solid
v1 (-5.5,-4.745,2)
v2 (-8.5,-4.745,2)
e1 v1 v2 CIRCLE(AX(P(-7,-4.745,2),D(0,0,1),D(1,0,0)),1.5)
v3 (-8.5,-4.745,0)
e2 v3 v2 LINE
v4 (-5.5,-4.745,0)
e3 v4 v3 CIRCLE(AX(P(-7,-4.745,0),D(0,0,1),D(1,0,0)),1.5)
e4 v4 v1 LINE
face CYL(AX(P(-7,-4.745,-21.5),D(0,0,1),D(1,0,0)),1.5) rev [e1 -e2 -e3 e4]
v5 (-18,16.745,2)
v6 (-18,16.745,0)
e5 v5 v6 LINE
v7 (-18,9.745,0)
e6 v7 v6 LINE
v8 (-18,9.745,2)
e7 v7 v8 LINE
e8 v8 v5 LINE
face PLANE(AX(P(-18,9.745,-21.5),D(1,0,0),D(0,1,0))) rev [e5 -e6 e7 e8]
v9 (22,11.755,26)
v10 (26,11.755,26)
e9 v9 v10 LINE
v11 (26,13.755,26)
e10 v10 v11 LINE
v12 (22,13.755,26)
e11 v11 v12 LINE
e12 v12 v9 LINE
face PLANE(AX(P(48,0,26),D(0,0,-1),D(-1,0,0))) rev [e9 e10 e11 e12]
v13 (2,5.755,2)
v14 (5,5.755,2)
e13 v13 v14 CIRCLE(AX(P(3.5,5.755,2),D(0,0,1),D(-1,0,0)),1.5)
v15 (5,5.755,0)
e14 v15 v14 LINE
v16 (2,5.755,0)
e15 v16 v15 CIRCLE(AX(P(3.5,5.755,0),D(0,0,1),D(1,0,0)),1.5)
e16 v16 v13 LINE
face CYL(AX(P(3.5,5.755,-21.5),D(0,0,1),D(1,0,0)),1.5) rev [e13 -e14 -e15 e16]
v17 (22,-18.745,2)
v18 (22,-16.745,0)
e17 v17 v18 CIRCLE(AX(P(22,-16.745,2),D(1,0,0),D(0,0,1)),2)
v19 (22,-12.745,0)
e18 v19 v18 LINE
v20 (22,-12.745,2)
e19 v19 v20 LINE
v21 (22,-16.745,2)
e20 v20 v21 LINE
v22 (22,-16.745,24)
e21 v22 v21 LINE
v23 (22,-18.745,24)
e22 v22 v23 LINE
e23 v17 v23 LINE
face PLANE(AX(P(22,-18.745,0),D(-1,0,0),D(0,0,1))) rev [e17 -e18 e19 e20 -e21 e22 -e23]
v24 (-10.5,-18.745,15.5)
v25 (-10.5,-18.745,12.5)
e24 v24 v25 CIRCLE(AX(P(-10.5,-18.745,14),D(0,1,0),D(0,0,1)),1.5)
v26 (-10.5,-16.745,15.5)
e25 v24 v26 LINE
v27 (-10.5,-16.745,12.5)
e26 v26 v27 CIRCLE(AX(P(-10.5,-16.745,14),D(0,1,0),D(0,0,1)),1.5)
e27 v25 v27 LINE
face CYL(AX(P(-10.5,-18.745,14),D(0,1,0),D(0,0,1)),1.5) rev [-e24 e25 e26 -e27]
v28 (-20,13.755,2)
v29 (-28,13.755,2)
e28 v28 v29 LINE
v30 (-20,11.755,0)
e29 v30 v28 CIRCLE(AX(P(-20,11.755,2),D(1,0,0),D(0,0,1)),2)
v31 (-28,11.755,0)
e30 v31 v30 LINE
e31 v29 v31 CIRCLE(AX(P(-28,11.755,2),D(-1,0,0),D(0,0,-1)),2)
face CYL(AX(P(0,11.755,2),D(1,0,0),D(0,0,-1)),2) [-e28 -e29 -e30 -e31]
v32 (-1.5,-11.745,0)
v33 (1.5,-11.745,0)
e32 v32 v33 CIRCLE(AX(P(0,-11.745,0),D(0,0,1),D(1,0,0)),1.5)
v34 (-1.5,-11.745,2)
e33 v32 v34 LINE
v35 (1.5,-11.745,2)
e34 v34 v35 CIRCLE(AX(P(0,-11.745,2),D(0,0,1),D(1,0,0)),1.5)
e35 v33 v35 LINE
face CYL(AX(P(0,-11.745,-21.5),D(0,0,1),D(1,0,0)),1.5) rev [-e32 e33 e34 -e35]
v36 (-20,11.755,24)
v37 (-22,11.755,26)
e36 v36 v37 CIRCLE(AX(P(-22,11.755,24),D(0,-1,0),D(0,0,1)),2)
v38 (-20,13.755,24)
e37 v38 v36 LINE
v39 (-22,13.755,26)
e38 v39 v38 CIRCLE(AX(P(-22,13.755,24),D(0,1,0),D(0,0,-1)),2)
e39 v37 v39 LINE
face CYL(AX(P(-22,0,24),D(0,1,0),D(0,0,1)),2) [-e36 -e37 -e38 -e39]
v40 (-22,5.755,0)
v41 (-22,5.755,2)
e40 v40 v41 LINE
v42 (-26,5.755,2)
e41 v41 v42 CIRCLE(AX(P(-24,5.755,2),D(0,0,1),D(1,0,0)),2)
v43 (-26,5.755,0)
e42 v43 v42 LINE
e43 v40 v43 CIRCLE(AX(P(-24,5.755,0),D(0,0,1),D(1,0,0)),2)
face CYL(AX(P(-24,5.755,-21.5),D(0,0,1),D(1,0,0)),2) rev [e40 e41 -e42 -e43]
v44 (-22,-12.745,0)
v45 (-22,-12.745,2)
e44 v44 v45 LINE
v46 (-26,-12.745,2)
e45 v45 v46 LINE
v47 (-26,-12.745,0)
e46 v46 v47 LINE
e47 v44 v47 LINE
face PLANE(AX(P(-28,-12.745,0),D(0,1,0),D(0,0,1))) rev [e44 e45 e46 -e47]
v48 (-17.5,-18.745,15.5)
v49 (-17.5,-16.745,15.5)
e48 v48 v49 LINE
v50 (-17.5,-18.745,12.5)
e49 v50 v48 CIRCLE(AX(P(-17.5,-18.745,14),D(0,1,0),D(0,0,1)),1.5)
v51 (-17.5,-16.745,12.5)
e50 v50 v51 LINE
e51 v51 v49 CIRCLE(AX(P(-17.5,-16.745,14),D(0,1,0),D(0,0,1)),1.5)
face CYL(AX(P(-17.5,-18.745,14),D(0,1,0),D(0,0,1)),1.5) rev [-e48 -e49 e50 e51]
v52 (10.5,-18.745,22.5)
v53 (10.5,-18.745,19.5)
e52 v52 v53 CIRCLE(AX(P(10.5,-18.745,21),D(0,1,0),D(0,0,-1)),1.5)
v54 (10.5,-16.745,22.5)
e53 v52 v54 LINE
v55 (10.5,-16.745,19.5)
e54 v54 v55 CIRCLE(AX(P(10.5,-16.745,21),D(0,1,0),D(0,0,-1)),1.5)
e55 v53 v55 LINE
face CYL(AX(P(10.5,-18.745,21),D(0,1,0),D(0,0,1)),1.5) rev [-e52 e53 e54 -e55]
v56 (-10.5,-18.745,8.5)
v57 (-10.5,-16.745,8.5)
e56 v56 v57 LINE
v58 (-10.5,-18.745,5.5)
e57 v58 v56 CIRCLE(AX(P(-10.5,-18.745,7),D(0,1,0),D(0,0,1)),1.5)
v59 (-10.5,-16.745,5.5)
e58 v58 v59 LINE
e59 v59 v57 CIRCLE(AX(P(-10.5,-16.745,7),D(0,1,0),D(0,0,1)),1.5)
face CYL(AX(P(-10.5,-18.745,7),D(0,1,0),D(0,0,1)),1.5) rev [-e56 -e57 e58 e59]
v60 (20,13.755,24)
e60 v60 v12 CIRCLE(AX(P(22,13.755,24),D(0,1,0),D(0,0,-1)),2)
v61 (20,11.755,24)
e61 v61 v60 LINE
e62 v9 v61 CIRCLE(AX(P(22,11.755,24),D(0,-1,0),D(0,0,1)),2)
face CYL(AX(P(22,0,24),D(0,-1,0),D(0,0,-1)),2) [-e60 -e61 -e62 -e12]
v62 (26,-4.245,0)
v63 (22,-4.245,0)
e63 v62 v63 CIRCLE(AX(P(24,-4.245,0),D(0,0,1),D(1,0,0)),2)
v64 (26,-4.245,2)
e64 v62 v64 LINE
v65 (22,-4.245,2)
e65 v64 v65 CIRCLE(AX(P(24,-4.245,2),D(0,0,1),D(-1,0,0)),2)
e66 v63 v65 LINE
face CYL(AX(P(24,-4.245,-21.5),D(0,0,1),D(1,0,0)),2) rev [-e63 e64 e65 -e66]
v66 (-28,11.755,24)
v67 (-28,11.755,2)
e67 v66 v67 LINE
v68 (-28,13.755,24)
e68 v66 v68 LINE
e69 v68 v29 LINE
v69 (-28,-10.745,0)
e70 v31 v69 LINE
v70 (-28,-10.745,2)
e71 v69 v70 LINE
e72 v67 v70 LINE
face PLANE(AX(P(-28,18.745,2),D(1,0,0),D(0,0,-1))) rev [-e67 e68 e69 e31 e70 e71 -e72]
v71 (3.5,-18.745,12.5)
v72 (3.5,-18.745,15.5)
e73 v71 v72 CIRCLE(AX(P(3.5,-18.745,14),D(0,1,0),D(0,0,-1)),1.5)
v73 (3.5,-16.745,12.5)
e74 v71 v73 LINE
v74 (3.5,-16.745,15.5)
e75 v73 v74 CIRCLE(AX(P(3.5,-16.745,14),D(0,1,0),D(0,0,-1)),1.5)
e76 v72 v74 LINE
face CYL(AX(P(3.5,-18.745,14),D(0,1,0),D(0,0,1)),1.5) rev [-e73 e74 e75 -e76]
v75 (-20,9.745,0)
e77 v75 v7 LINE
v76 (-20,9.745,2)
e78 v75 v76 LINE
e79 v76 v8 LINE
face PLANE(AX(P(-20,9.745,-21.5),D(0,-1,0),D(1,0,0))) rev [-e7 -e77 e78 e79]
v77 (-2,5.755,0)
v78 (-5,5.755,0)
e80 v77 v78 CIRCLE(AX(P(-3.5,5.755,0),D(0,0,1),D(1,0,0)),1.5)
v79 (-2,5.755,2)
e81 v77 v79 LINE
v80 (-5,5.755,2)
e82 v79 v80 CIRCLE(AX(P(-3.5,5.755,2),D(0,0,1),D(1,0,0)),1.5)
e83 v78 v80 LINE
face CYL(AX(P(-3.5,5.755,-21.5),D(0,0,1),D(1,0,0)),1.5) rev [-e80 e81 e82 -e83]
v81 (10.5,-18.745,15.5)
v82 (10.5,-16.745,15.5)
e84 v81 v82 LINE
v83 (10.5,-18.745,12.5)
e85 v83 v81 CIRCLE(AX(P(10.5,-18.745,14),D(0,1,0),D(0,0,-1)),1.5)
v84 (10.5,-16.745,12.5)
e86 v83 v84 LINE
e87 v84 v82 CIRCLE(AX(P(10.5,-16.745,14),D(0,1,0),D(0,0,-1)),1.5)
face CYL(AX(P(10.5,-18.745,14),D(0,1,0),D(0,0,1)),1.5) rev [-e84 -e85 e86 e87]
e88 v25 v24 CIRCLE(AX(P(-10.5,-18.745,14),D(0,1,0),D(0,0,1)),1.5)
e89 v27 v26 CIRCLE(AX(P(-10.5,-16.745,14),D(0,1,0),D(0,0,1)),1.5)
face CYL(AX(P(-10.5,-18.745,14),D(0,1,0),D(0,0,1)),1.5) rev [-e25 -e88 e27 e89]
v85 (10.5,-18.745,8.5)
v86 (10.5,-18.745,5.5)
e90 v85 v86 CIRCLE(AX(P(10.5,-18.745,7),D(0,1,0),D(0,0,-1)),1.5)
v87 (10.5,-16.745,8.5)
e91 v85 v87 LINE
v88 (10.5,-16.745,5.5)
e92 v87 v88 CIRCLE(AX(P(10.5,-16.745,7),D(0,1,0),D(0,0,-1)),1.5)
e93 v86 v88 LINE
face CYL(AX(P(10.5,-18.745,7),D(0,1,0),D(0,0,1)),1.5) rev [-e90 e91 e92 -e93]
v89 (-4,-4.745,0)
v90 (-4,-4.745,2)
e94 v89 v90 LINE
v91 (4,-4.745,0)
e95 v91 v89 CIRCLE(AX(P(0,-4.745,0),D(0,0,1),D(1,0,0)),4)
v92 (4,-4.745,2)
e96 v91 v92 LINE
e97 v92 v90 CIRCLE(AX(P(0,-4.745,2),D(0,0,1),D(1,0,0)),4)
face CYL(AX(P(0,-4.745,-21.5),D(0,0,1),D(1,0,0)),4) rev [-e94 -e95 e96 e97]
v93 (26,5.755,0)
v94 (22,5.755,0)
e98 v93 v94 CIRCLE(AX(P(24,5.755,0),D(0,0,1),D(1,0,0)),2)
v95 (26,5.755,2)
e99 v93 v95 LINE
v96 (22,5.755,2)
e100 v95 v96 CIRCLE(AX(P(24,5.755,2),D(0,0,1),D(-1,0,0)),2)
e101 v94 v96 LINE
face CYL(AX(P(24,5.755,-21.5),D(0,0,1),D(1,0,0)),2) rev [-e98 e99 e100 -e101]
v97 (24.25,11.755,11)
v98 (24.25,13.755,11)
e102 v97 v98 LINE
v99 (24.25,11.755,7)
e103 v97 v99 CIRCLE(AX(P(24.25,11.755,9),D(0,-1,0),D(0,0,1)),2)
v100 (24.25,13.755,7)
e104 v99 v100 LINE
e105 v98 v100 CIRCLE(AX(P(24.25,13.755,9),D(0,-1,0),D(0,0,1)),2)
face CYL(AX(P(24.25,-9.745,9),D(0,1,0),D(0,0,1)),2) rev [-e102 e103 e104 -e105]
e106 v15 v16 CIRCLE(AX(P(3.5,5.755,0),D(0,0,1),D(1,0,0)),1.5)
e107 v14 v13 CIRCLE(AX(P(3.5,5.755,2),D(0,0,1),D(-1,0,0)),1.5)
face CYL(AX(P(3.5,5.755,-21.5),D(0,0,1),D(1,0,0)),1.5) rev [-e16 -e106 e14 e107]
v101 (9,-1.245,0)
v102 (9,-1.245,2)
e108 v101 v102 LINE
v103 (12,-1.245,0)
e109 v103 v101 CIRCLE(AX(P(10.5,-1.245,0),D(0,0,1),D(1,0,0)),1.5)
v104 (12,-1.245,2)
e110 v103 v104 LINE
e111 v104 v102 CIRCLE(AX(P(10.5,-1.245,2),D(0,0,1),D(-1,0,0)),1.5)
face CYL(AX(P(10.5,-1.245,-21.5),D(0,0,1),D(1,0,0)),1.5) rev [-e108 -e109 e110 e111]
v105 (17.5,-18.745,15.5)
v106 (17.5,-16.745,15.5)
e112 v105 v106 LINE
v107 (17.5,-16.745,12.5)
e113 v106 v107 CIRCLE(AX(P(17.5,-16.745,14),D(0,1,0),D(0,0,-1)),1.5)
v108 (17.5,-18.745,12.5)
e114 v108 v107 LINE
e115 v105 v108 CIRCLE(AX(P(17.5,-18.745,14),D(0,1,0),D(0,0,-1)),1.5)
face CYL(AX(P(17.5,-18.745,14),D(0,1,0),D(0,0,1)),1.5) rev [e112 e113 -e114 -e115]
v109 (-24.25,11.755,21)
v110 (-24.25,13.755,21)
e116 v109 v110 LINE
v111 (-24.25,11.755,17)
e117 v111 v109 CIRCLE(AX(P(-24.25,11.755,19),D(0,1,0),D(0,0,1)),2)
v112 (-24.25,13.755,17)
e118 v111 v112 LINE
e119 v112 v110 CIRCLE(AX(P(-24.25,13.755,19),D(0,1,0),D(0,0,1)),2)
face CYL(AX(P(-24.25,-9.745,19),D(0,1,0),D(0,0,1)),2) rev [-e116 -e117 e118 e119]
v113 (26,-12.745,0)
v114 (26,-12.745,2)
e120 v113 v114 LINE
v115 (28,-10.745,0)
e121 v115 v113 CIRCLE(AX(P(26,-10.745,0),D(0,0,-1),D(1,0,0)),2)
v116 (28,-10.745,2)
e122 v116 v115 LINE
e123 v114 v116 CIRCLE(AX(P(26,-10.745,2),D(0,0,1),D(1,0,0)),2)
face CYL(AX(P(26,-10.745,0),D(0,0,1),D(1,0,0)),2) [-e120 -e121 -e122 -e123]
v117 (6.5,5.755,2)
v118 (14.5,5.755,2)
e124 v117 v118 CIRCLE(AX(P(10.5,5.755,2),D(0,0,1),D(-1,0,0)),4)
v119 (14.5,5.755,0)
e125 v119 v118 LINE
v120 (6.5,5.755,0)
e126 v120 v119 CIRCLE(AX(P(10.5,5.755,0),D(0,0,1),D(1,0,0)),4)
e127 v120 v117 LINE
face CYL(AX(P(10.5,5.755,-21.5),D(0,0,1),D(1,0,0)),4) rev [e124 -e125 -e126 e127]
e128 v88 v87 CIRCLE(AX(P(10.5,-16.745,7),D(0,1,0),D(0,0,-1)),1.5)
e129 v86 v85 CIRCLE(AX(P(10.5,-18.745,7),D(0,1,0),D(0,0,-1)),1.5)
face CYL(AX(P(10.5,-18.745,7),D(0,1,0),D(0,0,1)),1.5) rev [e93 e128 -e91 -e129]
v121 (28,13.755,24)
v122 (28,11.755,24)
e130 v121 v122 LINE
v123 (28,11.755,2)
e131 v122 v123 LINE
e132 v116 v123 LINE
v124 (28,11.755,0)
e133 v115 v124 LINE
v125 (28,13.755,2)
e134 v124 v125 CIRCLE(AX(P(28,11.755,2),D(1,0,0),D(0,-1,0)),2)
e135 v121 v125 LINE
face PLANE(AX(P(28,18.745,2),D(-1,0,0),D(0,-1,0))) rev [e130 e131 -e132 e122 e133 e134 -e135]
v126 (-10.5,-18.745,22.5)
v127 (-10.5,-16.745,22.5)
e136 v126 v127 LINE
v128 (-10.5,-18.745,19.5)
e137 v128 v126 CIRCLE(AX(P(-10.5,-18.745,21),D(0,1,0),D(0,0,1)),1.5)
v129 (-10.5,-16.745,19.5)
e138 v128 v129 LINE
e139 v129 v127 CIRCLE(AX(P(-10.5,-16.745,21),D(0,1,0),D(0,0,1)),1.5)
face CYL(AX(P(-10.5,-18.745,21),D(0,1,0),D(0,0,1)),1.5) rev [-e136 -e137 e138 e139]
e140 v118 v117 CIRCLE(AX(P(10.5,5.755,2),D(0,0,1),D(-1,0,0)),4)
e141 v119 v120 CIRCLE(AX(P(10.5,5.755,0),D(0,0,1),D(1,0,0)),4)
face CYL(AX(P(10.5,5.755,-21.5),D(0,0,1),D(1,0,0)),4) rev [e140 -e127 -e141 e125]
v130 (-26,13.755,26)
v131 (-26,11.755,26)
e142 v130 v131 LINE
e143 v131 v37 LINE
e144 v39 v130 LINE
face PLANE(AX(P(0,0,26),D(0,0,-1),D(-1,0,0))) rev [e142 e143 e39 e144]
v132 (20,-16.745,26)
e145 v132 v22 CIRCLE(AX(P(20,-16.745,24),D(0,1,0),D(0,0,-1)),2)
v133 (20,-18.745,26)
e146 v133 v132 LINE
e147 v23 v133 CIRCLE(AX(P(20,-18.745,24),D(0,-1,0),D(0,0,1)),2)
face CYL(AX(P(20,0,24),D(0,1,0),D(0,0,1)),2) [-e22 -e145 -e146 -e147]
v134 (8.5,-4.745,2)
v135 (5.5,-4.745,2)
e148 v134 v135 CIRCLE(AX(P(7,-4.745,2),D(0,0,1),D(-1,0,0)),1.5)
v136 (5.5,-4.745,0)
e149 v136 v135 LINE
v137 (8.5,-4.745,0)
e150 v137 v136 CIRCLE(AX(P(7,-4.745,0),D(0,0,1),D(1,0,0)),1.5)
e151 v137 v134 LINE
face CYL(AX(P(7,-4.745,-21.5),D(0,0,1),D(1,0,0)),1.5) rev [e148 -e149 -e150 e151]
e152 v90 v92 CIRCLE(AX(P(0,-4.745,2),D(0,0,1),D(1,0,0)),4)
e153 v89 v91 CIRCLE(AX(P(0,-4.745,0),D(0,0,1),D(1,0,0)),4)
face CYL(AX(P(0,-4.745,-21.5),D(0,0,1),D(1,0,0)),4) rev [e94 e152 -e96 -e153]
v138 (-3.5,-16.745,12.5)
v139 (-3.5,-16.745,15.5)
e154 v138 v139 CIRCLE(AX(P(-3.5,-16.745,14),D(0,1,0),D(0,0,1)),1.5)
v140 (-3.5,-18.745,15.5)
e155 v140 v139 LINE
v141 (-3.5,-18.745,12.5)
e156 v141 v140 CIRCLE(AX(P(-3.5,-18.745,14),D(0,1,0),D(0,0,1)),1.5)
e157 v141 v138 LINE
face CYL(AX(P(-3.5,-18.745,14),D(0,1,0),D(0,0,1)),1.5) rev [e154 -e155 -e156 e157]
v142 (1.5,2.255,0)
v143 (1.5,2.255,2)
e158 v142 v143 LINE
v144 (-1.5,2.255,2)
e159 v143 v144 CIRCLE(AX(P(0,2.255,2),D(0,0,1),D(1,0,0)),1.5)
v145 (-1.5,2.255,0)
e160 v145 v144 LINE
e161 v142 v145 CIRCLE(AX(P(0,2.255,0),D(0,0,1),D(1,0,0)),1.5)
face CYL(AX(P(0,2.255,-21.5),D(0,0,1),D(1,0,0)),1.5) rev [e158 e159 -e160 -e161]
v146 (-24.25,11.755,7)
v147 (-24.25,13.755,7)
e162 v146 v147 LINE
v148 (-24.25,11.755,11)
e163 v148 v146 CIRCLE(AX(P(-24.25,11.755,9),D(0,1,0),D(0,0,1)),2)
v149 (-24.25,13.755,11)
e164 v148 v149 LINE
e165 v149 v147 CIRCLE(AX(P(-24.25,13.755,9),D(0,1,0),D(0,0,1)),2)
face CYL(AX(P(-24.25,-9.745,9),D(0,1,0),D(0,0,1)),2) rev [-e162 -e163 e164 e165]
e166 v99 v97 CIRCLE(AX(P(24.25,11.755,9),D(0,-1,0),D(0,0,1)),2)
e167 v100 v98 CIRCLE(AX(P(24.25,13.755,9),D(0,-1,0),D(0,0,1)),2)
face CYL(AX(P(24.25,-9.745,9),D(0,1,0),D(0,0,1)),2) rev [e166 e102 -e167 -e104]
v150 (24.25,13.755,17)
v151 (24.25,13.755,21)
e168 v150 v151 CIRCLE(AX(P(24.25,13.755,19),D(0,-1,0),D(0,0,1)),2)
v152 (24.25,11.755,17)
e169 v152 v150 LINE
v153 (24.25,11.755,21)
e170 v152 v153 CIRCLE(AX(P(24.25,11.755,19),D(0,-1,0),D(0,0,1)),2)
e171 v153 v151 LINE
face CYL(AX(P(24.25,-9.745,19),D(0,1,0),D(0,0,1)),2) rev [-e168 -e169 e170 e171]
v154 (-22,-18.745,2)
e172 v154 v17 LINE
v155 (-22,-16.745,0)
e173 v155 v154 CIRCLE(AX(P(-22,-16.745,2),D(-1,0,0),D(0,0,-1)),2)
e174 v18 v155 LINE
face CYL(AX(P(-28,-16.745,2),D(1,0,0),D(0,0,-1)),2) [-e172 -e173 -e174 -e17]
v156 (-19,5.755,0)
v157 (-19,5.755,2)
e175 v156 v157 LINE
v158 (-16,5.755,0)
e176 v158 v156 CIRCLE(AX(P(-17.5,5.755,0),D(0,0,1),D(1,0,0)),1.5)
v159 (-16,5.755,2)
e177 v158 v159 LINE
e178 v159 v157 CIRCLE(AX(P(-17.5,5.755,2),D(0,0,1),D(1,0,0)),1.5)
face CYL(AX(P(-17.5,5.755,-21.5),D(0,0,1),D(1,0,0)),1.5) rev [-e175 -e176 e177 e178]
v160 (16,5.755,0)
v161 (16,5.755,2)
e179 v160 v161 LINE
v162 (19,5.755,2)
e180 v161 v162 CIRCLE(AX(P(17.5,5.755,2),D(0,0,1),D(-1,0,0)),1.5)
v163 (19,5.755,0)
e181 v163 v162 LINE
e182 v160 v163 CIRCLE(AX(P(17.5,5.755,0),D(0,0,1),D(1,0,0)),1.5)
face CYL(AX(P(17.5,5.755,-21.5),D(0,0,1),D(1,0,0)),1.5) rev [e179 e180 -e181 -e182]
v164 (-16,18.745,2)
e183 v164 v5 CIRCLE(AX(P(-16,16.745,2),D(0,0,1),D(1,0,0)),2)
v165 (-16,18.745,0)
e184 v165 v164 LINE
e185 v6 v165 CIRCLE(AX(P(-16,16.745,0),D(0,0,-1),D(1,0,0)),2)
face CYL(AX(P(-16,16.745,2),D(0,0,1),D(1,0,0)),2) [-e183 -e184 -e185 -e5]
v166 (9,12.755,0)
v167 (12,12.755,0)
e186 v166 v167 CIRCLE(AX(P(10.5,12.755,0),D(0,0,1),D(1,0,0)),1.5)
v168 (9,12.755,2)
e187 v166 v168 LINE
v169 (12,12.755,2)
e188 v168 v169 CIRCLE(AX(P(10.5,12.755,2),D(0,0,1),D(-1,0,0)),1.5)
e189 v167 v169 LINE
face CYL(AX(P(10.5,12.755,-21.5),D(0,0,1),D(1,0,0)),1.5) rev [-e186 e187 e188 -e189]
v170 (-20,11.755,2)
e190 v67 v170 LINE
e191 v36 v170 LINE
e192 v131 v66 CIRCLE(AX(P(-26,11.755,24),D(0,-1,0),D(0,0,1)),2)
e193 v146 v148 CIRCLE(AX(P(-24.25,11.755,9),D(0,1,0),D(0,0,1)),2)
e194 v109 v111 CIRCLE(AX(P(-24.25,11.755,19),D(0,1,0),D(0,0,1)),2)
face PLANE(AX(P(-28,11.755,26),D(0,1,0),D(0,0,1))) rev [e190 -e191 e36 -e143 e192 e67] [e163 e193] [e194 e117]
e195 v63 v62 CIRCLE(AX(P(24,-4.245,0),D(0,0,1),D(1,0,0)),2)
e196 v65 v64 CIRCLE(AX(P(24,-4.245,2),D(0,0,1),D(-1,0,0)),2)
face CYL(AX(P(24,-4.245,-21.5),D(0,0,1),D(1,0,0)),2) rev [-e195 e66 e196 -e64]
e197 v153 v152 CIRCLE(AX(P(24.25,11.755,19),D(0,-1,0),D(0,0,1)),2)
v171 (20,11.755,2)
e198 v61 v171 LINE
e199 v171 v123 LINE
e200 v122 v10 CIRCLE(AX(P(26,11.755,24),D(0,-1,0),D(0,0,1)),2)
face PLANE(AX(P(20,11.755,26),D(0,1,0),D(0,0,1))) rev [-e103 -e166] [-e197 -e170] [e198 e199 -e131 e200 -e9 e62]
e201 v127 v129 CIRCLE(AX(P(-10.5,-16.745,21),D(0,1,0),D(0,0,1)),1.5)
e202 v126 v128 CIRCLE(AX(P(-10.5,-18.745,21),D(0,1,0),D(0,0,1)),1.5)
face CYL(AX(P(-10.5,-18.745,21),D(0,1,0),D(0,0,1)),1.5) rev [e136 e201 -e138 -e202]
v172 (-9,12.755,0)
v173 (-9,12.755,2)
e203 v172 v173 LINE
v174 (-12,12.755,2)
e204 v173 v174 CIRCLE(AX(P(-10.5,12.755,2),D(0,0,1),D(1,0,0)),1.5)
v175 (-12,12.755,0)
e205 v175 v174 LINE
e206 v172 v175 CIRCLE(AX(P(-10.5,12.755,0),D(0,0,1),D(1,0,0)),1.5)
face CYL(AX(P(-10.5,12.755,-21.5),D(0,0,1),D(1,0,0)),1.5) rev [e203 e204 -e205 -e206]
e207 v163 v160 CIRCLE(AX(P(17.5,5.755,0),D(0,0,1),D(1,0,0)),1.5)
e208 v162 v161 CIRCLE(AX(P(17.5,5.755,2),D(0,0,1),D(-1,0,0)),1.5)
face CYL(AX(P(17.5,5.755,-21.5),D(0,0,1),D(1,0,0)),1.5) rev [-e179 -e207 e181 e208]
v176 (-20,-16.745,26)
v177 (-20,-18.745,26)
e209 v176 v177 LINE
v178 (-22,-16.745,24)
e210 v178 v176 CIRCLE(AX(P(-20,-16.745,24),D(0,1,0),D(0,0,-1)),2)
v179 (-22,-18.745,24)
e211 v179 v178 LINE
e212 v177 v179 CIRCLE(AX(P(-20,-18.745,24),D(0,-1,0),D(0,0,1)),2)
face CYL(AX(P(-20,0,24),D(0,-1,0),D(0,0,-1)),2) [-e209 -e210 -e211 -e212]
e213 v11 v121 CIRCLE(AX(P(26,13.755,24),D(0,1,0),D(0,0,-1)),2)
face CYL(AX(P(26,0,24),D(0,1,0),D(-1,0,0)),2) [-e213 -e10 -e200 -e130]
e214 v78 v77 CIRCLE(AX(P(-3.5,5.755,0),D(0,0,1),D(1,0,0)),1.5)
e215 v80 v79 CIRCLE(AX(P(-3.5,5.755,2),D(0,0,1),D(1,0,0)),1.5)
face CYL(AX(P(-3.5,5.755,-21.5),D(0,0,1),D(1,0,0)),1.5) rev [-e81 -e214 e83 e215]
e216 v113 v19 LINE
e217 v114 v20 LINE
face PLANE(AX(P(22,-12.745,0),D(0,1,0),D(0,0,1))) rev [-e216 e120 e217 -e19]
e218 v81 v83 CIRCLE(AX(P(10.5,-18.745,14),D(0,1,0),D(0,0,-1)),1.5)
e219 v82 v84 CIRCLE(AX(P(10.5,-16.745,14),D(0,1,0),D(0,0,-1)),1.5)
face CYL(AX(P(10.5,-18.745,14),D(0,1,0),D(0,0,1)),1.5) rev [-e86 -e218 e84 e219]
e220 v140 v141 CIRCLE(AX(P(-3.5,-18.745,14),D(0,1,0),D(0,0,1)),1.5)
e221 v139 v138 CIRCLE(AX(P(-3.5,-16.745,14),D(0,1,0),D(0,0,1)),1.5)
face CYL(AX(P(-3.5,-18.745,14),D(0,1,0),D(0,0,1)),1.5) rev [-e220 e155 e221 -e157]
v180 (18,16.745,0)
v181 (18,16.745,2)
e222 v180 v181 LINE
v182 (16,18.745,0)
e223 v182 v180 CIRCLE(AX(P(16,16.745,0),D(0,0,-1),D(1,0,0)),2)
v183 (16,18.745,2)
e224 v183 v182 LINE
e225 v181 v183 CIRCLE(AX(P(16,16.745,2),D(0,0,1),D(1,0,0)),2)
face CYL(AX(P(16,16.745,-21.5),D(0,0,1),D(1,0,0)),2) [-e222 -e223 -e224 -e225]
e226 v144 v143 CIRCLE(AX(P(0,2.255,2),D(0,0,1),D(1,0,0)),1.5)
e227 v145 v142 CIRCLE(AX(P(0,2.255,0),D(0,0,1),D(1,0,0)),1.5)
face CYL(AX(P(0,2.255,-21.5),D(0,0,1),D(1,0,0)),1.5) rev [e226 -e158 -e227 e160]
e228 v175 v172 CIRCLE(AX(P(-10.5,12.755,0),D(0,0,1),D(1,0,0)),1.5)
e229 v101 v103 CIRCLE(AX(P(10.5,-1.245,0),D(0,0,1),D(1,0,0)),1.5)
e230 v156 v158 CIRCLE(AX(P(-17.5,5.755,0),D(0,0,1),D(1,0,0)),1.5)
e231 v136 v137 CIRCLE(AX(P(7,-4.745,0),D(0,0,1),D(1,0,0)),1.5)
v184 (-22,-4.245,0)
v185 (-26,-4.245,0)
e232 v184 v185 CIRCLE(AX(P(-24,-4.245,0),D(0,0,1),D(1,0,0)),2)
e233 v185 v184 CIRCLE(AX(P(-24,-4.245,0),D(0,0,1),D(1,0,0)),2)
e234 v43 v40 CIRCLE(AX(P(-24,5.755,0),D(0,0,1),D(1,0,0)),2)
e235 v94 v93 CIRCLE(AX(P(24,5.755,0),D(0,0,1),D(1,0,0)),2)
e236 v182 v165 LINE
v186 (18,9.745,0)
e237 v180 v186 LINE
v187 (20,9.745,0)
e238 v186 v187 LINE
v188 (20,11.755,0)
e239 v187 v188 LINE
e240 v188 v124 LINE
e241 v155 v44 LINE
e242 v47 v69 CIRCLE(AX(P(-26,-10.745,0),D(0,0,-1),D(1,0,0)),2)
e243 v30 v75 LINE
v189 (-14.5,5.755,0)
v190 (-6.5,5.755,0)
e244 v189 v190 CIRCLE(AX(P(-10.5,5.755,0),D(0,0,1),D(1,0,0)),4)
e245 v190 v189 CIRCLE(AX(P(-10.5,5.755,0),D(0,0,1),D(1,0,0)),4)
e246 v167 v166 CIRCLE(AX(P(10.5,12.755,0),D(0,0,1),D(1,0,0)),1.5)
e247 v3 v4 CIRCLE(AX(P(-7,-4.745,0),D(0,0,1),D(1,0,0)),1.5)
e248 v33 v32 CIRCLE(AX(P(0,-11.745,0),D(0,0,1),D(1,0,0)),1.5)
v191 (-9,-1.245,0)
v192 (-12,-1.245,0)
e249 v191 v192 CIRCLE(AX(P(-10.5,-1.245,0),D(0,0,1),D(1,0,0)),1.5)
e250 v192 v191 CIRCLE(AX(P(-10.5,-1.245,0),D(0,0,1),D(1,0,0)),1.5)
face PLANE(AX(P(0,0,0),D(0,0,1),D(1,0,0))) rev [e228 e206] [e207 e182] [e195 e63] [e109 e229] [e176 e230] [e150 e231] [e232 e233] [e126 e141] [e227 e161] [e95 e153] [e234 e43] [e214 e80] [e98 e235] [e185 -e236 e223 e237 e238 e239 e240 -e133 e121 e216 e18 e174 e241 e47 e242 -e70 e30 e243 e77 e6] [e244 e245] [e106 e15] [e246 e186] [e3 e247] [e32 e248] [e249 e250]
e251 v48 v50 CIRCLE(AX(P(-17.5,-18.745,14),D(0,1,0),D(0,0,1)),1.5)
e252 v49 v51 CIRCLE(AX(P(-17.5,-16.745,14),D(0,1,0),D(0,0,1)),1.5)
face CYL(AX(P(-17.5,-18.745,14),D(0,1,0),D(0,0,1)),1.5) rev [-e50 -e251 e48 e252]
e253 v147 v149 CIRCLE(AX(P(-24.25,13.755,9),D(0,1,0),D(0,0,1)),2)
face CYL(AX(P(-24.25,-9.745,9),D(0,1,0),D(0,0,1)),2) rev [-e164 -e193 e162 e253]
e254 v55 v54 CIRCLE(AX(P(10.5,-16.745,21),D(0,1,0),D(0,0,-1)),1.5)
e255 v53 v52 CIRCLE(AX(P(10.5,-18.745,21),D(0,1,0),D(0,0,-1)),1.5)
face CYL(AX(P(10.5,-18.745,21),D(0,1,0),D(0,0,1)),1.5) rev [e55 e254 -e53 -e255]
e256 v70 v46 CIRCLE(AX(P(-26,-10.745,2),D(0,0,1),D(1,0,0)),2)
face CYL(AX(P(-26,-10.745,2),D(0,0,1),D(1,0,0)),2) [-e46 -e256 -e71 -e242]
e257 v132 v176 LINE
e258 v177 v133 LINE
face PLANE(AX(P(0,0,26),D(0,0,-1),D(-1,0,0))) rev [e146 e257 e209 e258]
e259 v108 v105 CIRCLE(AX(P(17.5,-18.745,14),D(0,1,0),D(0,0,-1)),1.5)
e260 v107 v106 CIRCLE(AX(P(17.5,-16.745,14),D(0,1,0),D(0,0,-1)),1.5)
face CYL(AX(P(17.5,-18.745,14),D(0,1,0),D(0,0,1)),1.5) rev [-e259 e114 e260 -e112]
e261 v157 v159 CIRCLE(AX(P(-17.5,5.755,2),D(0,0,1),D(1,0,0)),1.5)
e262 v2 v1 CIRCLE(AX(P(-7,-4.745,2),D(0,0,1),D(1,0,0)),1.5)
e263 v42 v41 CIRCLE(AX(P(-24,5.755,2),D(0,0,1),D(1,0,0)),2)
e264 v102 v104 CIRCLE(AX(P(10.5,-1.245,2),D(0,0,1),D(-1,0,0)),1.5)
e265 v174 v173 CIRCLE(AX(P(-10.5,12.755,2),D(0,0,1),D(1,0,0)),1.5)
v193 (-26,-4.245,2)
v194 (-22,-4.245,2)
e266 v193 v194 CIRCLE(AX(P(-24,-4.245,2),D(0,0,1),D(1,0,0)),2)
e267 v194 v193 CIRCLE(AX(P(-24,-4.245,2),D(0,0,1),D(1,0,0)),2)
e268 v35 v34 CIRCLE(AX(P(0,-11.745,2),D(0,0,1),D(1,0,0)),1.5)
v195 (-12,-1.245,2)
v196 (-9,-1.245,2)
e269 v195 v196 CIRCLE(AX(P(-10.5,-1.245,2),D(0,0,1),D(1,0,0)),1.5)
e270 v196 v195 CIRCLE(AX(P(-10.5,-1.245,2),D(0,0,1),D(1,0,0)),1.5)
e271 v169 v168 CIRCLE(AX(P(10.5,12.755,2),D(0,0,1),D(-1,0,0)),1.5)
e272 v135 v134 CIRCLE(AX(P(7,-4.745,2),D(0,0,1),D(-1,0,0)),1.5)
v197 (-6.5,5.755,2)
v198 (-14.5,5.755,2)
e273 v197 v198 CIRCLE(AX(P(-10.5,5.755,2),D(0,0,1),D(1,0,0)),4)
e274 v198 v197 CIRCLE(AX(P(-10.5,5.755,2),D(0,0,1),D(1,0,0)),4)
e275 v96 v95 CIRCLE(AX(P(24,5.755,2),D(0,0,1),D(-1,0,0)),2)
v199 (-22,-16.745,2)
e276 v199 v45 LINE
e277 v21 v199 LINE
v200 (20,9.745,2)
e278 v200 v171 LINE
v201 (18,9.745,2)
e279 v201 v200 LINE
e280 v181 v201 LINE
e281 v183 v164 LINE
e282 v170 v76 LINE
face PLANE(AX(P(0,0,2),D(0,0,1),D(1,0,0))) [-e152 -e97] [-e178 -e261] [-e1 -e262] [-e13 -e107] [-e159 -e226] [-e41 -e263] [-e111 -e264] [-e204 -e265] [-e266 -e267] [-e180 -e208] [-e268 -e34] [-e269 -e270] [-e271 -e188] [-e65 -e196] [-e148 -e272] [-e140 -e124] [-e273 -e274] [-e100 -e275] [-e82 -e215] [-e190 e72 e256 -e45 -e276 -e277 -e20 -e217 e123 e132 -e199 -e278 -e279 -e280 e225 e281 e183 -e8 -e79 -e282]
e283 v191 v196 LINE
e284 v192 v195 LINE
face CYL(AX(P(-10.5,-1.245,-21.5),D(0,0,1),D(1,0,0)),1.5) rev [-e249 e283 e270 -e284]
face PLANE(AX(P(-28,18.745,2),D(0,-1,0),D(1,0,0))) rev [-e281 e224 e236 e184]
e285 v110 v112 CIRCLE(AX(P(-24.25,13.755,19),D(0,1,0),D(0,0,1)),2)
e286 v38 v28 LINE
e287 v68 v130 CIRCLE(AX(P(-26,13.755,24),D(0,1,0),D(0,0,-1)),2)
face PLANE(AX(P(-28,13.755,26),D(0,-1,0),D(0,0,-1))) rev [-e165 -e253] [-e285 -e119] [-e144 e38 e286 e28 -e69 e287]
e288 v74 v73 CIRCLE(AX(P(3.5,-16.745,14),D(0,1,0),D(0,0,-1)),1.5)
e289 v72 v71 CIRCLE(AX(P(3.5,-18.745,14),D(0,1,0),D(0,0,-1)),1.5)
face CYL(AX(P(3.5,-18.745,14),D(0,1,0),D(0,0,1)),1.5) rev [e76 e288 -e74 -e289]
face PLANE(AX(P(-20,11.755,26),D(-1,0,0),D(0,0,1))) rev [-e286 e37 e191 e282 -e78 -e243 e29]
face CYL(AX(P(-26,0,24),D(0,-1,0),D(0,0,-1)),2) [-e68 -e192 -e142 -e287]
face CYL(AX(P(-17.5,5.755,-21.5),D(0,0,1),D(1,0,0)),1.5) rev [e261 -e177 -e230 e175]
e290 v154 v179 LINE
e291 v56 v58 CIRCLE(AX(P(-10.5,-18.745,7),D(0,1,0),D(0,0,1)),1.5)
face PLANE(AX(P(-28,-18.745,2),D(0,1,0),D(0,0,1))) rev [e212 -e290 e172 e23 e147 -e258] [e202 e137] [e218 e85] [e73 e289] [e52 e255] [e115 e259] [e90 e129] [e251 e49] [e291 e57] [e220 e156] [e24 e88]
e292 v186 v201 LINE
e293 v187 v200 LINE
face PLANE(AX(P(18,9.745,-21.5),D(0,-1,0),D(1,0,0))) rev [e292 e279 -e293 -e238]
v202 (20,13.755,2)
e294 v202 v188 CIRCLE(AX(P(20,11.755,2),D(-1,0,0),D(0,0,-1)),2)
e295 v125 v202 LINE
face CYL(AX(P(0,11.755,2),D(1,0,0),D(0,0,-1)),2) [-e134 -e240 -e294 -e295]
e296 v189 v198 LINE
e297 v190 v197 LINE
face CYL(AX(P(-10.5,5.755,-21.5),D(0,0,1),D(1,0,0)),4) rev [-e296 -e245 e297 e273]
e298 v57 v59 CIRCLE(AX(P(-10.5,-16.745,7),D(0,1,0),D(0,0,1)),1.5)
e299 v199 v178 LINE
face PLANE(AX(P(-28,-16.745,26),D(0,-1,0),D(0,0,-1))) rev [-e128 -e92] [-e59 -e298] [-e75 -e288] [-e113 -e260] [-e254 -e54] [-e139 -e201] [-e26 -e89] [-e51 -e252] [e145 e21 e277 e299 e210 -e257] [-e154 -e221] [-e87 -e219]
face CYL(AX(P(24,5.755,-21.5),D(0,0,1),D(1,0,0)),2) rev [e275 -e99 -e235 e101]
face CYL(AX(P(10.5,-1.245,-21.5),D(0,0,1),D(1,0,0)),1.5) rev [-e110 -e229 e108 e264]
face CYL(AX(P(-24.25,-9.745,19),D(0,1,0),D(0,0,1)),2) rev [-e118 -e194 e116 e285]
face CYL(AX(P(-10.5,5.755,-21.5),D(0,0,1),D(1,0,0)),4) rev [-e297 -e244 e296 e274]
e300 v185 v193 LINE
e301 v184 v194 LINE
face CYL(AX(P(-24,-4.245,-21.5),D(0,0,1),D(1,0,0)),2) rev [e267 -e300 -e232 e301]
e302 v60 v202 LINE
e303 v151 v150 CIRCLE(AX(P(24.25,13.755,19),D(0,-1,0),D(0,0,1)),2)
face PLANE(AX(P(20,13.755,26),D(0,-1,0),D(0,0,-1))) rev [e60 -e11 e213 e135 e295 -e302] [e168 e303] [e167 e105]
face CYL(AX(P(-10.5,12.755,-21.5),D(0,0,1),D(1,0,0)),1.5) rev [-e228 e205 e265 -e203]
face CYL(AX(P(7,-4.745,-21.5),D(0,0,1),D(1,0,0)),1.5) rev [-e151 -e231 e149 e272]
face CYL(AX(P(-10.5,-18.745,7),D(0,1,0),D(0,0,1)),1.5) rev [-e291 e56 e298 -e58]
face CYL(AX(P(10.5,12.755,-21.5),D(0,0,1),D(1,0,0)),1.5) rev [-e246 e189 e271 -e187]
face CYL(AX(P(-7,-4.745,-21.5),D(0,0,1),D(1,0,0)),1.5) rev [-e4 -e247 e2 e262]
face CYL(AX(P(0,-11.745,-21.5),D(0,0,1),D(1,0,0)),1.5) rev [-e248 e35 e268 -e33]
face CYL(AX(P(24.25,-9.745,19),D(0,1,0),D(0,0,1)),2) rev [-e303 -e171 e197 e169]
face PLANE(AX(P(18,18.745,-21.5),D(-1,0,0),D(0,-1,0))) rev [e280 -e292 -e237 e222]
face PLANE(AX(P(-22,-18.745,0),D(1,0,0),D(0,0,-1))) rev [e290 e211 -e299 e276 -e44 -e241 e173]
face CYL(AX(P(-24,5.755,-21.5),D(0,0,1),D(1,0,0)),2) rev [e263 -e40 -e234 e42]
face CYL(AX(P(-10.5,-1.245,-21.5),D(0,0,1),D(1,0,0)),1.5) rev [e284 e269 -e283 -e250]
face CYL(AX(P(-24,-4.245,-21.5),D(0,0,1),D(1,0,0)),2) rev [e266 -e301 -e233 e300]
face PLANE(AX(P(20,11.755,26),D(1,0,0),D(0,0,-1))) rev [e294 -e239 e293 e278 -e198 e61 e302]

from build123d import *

# Parameters (mm, degrees)
SKETCH3_W           = 56
SKETCH3_H           = 37.49
BOSS_EXTRUDE1_DEPTH = 2
SKETCH4_W           = 56
SKETCH4_H           = 2
BOSS_EXTRUDE2_DEPTH = 24
SKETCH5_W           = 8
SKETCH5_H           = 2
BOSS_EXTRUDE3_DEPTH = 24
LINPATTERN1_COUNT   = 2
LINPATTERN1_PITCH   = 48
SKETCH6_W           = 6
SKETCH6_H           = 6
CUT_EXTRUDE1_DEPTH  = 42.368768715
LINPATTERN2_COUNT   = 2
LINPATTERN2_PITCH   = 50
CUT_EXTRUDE2_DEPTH  = 23.5
CUT_EXTRUDE3_DEPTH  = 23.5
SKETCH9_R           = 2
SKETCH9_R_2         = 4
SKETCH9_R_3         = 1.5
CUT_EXTRUDE4_DEPTH  = 23.5
SKETCH11_R          = 1.5
CUT_EXTRUDE5_DEPTH  = 53.149209965
FILLET1_R           = 2
SKETCH12_R          = 2
CUT_EXTRUDE6_DEPTH  = 23.5


with BuildPart() as part:
    # Sketch3 → Boss-Extrude1 (new body)
    with BuildSketch(Plane.XY):
        Rectangle(SKETCH3_W, SKETCH3_H)
    extrude(amount=BOSS_EXTRUDE1_DEPTH)

    # Sketch4 → Boss-Extrude2 (add)
    with BuildSketch(Plane.XY.offset(2)):
        with Locations((0, -17.745)):
            Rectangle(SKETCH4_W, SKETCH4_H)
    extrude(amount=BOSS_EXTRUDE2_DEPTH)

    # Sketch5 → Boss-Extrude3 (add)
    with BuildSketch(Plane.XY.offset(2)):
        with Locations((-24, 12.755)):
            Rectangle(SKETCH5_W, SKETCH5_H)
    boss_extrude3 = extrude(amount=BOSS_EXTRUDE3_DEPTH)

    # LinPattern1: Boss-Extrude3 ×2
    with Locations(*[(i * LINPATTERN1_PITCH, 0, 0) for i in range(1, LINPATTERN1_COUNT)]):
        add(boss_extrude3)

    # Sketch6 → Cut-Extrude1 (cut, symmetric)
    with BuildSketch(Plane.XY.offset(2)):
        with Locations((-25, -15.745)):
            Rectangle(SKETCH6_W, SKETCH6_H)
    cut_extrude1 = extrude(amount=CUT_EXTRUDE1_DEPTH, both=True, mode=Mode.SUBTRACT)

    # LinPattern2: Cut-Extrude1 ×2
    with Locations(*[(i * LINPATTERN2_PITCH, 0, 0) for i in range(1, LINPATTERN2_COUNT)]):
        add(cut_extrude1, mode=Mode.SUBTRACT)

    # Sketch7 → Cut-Extrude2 (cut)
    with BuildSketch(Plane.XY.offset(2)):
        Polygon((-28, 18.745), (-28, 13.755), (-20, 13.755), (-20, 11.755), (-20, 9.745), (-18, 9.745), (-18, 18.745), align=None)
    extrude(amount=-CUT_EXTRUDE2_DEPTH, mode=Mode.SUBTRACT)

    # Sketch8 → Cut-Extrude3 (cut)
    with BuildSketch(Plane.XY.offset(2)):
        Polygon((28, 13.755), (28, 18.745), (18, 18.745), (18, 9.745), (20, 9.745), (20, 13.755), align=None)
    extrude(amount=-CUT_EXTRUDE3_DEPTH, mode=Mode.SUBTRACT)

    # Sketch9 → Cut-Extrude4 (cut)
    with BuildSketch(Plane.XY.offset(2)):
        with Locations((-24, 5.755)):
            Circle(SKETCH9_R)
        with Locations((-24, -4.245)):
            Circle(SKETCH9_R)
        with Locations((-10.5, 5.755)):
            Circle(SKETCH9_R_2)
        with Locations((0, -4.745)):
            Circle(SKETCH9_R_2)
        with Locations((0, 2.255)):
            Circle(SKETCH9_R_3)
        with Locations((0, -11.745)):
            Circle(SKETCH9_R_3)
        with Locations((-10.5, -1.245)):
            Circle(SKETCH9_R_3)
        with Locations((-10.5, 12.755)):
            Circle(SKETCH9_R_3)
        with Locations((-17.5, 5.755)):
            Circle(SKETCH9_R_3)
        with Locations((-3.5, 5.755)):
            Circle(SKETCH9_R_3)
        with Locations((-7, -4.745)):
            Circle(SKETCH9_R_3)
        with Locations((7, -4.745)):
            Circle(SKETCH9_R_3)
        with Locations((10.5, 12.755)):
            Circle(SKETCH9_R_3)
        with Locations((3.5, 5.755)):
            Circle(SKETCH9_R_3)
        with Locations((10.5, -1.245)):
            Circle(SKETCH9_R_3)
        with Locations((10.5, 5.755)):
            Circle(SKETCH9_R_2)
        with Locations((17.5, 5.755)):
            Circle(SKETCH9_R_3)
        with Locations((24, -4.245)):
            Circle(SKETCH9_R)
        with Locations((24, 5.755)):
            Circle(SKETCH9_R)
    extrude(amount=-CUT_EXTRUDE4_DEPTH, mode=Mode.SUBTRACT)

    # Sketch11 → Cut-Extrude5 (cut, through all)
    with BuildSketch(Plane(origin=(0, -16.745, 0), x_dir=(1, 0, 0), z_dir=(0, 1, 0))):
        with Locations(Location((-10.5, -14, 0), (0, 0, 270))):
            Circle(SKETCH11_R)
        with Locations(Location((-17.5, -14, 0), (0, 0, 270))):
            Circle(SKETCH11_R)
        with Locations(Location((-10.5, -21, 0), (0, 0, 270))):
            Circle(SKETCH11_R)
        with Locations(Location((-3.5, -14, 0), (0, 0, 270))):
            Circle(SKETCH11_R)
        with Locations(Location((-10.5, -7, 0), (0, 0, 270))):
            Circle(SKETCH11_R)
        with Locations(Location((10.5, -21, 0), (0, 0, 90))):
            Circle(SKETCH11_R)
        with Locations(Location((3.5, -14, 0), (0, 0, 90))):
            Circle(SKETCH11_R)
        with Locations(Location((10.5, -7, 0), (0, 0, 90))):
            Circle(SKETCH11_R)
        with Locations(Location((10.5, -14, 0), (0, 0, 90))):
            Circle(SKETCH11_R)
        with Locations(Location((17.5, -14, 0), (0, 0, 90))):
            Circle(SKETCH11_R)
    extrude(amount=-CUT_EXTRUDE5_DEPTH, mode=Mode.SUBTRACT)

    # Fillet1
    fillet1_edges = [part.edges().sort_by_distance(p)[0] for p in [
        (-24, 13.755, 0),
        (-18, 18.745, 1),
        (24, 13.755, 0),
        (18, 18.745, 1),
        (-28, 12.755, 26),
        (-20, 12.755, 26),
        (20, 12.755, 26),
        (28, 12.755, 26),
        (-22, -17.745, 26),
        (0, -18.745, 0),
        (-28, -12.745, 1),
        (22, -17.745, 26),
        (28, -12.745, 1),
    ]]
    fillet(fillet1_edges, radius=FILLET1_R)

    # Sketch12 → Cut-Extrude6 (cut)
    with BuildSketch(Plane(origin=(0, 13.755, 0), x_dir=(1, 0, 0), z_dir=(0, 1, 0))):
        with Locations(Location((-24.25, -19, 0), (0, 0, 270))):
            Circle(SKETCH12_R)
        with Locations(Location((-24.25, -9, 0), (0, 0, 270))):
            Circle(SKETCH12_R)
    cut_extrude6 = extrude(amount=-CUT_EXTRUDE6_DEPTH, mode=Mode.SUBTRACT)

    # Mirror2: Cut-Extrude6 across plane
    add(cut_extrude6.mirror(Plane(origin=(0, 0, 0), x_dir=(0, 0, 1), z_dir=(1, 0, 0))), mode=Mode.SUBTRACT)


solid = part.part
